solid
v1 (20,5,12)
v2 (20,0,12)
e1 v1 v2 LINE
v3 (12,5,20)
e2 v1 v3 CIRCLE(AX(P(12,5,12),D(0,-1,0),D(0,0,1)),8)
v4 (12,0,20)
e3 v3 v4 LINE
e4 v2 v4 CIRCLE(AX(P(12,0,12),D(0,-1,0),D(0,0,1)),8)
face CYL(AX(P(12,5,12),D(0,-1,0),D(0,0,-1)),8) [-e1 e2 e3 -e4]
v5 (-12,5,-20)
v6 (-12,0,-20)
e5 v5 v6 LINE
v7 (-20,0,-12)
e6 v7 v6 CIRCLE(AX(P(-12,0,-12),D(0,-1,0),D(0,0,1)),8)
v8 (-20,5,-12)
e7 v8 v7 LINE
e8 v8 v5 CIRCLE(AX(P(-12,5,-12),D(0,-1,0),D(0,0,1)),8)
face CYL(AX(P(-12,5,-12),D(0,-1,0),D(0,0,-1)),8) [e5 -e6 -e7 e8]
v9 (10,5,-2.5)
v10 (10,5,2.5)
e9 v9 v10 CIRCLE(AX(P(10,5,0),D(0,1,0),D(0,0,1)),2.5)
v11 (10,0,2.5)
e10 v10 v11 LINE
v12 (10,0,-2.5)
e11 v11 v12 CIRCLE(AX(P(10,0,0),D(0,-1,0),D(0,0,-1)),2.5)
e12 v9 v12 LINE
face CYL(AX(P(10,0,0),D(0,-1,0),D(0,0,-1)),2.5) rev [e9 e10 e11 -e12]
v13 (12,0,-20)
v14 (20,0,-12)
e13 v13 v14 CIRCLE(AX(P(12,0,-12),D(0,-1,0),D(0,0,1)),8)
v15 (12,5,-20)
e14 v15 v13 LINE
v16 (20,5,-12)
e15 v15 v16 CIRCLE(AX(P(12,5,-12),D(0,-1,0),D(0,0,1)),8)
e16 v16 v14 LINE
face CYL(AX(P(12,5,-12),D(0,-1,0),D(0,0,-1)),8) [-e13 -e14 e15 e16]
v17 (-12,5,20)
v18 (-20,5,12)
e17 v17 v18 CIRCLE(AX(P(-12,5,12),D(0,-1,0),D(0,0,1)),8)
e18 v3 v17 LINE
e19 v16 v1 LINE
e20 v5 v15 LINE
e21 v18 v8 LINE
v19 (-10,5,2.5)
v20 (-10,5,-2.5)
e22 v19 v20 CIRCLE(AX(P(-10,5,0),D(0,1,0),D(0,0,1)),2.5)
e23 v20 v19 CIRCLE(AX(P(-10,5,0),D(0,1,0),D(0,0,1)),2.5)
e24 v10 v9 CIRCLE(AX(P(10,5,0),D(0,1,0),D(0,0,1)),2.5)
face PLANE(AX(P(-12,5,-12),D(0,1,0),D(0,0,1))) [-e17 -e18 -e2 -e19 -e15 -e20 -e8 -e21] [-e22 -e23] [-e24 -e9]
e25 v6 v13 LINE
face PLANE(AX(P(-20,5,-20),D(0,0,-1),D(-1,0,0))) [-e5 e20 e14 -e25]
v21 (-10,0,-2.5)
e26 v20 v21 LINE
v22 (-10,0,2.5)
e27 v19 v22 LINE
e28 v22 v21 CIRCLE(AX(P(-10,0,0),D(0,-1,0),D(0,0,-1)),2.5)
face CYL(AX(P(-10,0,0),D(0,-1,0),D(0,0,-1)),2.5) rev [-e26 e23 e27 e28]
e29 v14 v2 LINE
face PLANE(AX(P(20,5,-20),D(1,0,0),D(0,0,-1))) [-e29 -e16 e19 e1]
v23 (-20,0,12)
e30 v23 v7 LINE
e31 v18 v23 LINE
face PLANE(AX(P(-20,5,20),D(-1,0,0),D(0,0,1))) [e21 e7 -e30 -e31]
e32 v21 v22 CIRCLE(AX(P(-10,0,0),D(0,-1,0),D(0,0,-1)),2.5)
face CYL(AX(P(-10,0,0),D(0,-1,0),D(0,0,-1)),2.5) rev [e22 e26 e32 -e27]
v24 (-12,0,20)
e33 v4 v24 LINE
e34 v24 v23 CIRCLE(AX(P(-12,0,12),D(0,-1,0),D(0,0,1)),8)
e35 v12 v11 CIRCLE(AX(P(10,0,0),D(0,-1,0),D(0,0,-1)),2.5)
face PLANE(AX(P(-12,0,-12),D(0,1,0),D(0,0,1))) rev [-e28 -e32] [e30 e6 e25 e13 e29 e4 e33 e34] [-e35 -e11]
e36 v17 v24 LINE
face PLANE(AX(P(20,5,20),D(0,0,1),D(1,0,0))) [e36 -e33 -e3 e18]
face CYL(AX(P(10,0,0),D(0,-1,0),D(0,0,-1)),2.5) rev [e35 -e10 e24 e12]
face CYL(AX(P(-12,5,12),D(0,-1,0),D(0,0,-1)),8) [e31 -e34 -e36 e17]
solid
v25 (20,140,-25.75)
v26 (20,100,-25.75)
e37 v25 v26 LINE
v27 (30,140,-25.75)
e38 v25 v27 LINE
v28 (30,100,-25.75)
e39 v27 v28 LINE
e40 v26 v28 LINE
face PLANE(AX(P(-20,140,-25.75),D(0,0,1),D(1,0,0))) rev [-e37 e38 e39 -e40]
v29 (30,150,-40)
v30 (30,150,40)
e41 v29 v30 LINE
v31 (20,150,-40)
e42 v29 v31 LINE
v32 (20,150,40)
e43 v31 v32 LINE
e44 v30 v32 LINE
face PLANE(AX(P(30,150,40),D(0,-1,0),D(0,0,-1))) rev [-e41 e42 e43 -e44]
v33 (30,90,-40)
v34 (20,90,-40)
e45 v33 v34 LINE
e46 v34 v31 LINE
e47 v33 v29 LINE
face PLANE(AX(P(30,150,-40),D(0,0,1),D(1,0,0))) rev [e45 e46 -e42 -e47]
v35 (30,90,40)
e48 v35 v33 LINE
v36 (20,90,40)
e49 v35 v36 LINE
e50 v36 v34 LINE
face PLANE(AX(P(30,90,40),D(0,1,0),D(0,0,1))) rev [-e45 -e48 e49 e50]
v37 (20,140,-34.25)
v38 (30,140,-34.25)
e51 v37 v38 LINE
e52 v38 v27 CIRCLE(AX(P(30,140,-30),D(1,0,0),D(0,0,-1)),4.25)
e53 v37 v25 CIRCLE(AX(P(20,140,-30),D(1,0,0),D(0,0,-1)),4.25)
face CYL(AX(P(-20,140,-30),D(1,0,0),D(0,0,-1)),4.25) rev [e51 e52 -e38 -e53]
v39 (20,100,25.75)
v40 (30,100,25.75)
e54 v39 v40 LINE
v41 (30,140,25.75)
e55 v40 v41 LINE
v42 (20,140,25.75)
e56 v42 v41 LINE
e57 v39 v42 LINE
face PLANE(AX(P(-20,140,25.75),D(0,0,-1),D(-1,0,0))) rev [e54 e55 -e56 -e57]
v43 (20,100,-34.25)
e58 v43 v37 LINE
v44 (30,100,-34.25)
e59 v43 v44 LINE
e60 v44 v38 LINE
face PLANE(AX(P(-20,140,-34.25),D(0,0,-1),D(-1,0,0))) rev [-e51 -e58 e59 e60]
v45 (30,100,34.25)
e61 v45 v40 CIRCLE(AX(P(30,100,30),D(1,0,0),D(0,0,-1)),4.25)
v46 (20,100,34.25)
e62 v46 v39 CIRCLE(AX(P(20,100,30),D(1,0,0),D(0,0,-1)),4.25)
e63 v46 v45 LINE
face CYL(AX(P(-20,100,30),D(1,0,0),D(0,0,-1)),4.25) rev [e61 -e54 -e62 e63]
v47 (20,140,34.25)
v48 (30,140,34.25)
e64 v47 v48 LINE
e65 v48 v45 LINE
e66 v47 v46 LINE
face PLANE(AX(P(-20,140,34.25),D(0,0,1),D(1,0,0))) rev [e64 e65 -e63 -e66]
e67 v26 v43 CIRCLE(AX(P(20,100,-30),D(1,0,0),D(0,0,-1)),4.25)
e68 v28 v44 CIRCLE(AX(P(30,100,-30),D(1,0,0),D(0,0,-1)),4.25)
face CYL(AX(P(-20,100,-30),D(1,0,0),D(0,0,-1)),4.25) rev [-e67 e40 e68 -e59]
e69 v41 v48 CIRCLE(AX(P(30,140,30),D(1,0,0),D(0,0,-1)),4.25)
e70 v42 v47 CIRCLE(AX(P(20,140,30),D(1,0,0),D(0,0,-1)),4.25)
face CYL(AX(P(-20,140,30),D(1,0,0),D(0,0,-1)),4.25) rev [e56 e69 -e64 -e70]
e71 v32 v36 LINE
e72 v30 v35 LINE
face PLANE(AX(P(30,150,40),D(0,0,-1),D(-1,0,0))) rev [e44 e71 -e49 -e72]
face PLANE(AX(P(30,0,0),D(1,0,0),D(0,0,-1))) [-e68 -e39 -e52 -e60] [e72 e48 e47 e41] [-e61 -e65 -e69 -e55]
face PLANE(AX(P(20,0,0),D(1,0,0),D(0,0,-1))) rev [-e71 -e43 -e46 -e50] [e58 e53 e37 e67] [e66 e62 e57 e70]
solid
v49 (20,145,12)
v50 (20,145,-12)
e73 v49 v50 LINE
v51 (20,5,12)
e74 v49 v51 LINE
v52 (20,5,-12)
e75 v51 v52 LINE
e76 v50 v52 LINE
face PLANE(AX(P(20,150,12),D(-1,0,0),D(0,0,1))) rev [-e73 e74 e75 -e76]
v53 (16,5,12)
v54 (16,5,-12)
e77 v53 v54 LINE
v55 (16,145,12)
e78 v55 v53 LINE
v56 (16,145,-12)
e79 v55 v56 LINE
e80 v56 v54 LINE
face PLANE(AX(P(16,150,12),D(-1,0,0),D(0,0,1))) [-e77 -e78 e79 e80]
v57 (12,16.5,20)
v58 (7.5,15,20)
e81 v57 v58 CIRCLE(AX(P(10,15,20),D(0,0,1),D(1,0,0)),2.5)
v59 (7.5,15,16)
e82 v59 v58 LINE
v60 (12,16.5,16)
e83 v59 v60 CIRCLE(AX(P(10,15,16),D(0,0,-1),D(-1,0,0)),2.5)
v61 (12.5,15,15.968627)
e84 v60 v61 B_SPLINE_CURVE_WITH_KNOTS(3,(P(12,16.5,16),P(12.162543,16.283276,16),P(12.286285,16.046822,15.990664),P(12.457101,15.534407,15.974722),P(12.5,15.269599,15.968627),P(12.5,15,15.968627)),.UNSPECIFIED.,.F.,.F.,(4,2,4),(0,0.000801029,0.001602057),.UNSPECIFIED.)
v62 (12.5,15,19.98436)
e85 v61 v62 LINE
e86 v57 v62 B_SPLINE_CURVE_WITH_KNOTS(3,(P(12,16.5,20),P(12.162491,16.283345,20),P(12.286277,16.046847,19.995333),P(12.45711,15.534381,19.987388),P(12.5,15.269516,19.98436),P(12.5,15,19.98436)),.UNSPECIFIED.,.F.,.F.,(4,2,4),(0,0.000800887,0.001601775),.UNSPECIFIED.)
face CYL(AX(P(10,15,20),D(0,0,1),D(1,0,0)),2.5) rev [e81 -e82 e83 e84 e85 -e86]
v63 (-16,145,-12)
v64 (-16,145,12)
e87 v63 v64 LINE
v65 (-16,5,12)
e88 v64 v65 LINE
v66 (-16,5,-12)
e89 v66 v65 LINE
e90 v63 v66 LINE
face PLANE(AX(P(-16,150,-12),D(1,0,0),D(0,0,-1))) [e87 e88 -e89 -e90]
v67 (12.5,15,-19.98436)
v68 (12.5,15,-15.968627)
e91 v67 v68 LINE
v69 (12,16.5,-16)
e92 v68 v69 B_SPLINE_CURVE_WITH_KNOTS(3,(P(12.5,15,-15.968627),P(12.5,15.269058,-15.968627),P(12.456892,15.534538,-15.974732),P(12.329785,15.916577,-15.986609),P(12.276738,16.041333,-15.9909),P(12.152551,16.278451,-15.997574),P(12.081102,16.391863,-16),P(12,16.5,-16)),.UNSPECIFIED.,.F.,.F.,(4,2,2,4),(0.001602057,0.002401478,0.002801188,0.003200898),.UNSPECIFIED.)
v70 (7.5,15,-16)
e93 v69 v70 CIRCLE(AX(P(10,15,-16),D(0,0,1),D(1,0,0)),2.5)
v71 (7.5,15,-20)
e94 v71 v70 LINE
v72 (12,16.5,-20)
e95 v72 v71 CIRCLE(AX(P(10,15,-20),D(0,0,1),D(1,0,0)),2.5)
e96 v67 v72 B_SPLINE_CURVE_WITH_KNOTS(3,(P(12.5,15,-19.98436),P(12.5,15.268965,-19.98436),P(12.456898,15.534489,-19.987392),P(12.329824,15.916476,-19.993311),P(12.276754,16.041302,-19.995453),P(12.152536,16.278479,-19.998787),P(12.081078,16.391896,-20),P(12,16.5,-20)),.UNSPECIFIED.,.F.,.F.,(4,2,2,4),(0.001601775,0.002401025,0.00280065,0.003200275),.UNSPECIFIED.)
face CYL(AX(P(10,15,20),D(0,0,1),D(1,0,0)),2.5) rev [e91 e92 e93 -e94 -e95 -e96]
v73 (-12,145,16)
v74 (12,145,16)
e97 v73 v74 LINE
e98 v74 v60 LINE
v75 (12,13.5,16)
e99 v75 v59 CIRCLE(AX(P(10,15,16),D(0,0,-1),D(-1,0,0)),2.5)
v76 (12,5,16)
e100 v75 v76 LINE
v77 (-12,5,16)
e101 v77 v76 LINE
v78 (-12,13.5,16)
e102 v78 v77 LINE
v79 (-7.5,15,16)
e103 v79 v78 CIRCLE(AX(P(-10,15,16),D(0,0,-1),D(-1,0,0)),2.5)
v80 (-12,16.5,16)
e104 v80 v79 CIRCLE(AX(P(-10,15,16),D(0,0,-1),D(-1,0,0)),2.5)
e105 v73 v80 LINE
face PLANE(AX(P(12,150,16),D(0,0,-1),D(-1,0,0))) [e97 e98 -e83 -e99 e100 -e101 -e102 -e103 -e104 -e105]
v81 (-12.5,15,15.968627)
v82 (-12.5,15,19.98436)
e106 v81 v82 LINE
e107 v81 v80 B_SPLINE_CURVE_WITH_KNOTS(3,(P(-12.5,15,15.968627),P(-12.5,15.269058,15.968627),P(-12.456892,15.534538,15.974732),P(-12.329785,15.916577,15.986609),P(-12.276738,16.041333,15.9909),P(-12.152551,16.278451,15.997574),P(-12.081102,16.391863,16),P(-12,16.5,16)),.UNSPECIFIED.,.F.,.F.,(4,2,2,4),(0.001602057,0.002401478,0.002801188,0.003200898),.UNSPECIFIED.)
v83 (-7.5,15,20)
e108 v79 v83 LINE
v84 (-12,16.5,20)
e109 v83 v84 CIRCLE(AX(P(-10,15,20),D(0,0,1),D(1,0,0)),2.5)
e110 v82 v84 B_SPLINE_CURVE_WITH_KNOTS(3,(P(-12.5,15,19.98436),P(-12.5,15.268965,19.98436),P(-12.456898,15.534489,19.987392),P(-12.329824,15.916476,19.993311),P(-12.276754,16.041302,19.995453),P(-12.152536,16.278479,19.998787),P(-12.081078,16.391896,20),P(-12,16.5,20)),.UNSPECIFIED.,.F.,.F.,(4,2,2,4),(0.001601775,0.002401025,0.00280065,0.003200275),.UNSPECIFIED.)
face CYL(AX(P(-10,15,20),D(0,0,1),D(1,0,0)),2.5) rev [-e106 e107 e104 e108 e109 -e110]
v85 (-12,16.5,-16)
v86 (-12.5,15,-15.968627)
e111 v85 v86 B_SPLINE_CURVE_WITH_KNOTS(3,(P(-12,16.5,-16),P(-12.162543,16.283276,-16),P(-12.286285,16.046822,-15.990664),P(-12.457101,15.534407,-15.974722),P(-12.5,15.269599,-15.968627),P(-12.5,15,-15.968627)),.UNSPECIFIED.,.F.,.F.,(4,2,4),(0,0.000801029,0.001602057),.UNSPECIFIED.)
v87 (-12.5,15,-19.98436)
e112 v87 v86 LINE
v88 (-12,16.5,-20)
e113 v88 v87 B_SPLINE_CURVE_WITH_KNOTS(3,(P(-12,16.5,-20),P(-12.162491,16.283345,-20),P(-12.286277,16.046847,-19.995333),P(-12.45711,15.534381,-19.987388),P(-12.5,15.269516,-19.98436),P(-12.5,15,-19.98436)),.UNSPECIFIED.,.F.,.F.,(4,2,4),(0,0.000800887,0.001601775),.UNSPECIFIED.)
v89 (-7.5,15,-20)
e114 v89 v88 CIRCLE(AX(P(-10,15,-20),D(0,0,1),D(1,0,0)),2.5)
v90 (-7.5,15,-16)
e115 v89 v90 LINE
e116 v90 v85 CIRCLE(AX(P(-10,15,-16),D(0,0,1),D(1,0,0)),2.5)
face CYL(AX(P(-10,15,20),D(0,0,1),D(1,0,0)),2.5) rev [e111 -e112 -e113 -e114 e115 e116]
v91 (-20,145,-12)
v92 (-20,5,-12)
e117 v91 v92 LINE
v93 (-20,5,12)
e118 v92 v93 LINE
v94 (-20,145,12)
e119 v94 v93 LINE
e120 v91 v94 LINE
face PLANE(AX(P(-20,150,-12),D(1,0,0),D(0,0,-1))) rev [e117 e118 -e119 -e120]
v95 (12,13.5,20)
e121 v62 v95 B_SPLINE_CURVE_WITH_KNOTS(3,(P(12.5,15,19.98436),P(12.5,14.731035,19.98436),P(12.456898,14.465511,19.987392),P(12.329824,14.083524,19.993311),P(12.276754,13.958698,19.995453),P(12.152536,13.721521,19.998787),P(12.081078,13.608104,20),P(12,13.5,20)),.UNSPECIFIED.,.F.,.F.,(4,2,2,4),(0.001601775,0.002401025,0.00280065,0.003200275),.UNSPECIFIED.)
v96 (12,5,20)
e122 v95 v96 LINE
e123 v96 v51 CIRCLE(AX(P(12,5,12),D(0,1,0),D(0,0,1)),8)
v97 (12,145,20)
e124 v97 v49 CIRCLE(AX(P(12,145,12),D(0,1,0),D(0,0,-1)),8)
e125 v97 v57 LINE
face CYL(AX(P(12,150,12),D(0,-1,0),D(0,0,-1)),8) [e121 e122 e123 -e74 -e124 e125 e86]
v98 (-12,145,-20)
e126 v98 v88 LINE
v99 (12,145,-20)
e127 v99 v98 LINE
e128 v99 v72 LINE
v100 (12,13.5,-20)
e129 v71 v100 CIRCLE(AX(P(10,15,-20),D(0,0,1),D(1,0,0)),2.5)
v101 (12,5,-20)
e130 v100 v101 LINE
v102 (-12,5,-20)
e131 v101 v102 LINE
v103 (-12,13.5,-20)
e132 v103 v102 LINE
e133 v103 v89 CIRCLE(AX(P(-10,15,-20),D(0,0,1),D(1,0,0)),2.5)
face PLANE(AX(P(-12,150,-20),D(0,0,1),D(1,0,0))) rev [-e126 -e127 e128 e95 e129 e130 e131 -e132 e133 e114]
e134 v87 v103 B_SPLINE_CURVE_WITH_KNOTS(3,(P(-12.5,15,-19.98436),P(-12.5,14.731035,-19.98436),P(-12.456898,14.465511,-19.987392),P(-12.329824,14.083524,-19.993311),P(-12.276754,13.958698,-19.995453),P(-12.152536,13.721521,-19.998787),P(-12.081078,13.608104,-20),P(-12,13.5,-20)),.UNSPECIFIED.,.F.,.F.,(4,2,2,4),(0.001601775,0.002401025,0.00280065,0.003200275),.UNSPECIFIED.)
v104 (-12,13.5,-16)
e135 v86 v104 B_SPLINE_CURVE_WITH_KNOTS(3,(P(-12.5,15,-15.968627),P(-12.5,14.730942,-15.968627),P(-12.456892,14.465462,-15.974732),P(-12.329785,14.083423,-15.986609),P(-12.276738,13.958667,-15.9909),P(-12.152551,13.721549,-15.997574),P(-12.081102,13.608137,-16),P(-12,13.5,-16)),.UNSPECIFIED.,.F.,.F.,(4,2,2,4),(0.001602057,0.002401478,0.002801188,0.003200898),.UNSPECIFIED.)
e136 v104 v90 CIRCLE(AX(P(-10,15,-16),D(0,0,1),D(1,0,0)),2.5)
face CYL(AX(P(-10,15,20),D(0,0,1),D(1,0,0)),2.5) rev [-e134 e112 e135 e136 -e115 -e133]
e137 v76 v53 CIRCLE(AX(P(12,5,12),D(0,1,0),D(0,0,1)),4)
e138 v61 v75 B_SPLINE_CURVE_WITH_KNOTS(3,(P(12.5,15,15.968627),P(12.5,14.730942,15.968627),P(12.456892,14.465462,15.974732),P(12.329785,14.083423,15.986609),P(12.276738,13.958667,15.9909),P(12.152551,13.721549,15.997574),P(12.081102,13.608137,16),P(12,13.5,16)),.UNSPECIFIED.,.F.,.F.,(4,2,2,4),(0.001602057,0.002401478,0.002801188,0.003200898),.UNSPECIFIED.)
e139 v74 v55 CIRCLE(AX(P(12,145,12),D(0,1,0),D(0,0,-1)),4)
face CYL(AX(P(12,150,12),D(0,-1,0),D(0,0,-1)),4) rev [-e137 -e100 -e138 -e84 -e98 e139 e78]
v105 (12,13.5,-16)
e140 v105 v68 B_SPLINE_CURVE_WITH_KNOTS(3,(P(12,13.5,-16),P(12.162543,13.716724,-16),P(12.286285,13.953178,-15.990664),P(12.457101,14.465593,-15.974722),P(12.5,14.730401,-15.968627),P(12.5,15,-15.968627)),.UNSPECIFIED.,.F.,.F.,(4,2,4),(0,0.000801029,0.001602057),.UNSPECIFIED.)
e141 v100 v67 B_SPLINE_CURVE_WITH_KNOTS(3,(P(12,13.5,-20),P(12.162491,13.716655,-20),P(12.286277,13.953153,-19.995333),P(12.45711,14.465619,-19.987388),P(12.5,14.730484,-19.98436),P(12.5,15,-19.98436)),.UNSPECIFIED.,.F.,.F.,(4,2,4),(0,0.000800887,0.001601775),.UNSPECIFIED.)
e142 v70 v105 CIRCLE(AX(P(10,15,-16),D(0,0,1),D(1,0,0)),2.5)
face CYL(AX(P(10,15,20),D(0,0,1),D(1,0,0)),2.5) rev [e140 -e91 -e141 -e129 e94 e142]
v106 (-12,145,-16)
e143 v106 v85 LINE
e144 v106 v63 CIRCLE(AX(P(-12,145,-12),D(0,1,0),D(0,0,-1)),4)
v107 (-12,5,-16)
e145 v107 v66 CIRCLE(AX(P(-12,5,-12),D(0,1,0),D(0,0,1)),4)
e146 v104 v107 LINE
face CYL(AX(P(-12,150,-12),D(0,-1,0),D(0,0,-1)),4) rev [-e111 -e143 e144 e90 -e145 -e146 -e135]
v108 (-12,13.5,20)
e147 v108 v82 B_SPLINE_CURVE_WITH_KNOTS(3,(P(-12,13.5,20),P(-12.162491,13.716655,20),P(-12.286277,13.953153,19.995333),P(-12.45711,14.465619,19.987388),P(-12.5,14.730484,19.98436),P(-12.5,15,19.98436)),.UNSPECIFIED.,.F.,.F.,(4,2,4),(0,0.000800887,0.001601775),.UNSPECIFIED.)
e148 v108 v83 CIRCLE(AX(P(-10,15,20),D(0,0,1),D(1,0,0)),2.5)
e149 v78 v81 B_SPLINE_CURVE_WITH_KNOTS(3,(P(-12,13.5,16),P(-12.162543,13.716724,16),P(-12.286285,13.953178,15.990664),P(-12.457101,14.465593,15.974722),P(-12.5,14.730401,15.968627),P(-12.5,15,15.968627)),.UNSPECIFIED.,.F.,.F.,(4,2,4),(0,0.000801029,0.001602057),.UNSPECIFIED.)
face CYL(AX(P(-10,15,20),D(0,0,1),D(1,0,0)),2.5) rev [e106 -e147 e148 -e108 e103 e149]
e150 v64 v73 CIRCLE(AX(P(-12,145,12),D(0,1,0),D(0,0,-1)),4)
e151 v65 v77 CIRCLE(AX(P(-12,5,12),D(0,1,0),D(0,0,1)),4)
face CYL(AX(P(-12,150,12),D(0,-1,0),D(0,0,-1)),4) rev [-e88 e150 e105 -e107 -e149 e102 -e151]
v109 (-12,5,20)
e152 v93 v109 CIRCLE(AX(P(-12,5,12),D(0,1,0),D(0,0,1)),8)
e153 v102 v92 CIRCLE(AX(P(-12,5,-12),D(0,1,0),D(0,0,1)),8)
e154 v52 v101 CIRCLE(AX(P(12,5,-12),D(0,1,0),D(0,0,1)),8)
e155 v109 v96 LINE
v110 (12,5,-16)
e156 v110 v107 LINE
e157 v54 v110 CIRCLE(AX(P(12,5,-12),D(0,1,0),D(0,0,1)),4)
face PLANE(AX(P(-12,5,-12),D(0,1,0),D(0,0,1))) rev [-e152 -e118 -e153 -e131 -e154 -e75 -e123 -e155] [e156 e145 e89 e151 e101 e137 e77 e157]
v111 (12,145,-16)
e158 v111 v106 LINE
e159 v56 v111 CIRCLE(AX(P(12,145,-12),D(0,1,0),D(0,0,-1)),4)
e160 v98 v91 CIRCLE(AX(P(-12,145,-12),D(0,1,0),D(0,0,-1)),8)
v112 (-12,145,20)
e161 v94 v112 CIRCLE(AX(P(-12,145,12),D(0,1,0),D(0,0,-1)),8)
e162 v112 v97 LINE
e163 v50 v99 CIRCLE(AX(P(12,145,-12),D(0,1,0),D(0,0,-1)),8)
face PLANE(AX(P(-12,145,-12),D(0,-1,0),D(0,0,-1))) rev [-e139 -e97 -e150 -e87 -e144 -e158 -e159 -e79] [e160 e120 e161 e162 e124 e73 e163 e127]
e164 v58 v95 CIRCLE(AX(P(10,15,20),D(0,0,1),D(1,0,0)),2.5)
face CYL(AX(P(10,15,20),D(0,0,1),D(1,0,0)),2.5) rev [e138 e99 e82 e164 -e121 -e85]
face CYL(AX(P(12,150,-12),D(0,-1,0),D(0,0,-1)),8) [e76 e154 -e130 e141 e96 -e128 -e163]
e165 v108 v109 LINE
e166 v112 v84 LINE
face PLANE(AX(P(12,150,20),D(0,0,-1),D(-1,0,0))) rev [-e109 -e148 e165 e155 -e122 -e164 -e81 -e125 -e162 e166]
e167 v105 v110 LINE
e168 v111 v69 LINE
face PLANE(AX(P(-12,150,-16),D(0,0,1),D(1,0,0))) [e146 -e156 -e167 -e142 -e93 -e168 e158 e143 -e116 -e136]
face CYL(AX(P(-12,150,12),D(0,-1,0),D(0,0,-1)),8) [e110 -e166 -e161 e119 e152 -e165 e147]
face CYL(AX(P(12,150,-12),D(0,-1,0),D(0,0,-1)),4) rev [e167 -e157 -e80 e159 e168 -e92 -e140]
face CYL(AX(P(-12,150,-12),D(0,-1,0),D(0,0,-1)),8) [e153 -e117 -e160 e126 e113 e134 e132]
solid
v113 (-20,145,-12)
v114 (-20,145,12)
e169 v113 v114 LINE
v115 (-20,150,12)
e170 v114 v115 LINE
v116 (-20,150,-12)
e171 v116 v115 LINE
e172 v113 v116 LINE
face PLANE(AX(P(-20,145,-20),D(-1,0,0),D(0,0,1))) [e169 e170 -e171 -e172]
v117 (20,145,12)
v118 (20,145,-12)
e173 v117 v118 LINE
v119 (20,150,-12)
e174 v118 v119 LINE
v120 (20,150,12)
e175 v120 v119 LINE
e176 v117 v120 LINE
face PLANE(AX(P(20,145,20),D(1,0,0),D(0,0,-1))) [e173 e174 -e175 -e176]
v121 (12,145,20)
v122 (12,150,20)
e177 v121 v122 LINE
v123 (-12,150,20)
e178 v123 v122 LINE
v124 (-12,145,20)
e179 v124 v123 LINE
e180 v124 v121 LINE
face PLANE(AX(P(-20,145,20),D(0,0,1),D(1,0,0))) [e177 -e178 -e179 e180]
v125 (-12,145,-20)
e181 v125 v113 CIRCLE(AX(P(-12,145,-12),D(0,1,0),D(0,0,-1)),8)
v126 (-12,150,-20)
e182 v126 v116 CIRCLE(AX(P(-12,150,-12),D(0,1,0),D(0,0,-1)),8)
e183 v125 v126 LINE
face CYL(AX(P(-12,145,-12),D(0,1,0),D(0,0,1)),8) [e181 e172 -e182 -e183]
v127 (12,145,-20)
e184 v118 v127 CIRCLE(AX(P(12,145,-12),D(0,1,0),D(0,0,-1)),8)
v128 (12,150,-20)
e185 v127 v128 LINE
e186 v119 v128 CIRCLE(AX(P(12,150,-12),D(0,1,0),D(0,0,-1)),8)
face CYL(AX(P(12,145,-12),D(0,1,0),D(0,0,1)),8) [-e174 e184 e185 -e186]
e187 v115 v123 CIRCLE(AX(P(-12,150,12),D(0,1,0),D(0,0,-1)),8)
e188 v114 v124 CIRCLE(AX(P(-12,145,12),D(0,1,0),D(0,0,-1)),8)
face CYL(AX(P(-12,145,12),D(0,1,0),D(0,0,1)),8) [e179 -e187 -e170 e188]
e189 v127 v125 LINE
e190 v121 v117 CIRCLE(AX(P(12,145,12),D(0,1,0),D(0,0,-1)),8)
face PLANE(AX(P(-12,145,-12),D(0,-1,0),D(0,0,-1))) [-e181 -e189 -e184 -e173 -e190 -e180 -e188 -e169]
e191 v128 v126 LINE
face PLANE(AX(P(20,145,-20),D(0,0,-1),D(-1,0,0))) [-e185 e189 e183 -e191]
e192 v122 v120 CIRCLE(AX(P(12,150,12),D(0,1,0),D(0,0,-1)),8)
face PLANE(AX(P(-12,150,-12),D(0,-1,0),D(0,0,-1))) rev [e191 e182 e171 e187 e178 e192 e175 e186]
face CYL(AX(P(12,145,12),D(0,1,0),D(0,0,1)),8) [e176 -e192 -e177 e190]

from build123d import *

# Parameters (mm, degrees)
F_40_X_40_X_4_0_1_DEPTH     = 150
SKETCH_3_W                  = 80
SKETCH_3_H                  = 60
EXTRUDE_1_DEPTH             = 10
CUT_EXTRUDE_2_DEPTH         = 164.095064303
SKETCH_14_W                 = 2.5
SKETCH_14_H                 = 60
HOLE_WIZARD_M6_1_AT_2_COUNT = 2
HOLE_WIZARD_M6_1_AT_2_PITCH = 20
END_CAP_1_THICKNESS         = 5
HOLE_WIZARD_M6_2_AT_2_COUNT = 2
HOLE_WIZARD_M6_2_AT_2_PITCH = 20
END_CAP_2_THICKNESS         = 5


with BuildPart() as part:
    # Sketch1 → 方管 40 X 40 X 4.0(1) (new body)
    with BuildSketch(Plane.ZX):
        with BuildLine():
            Line((-12, -20), (12, -20))
            ThreePointArc((12, -20), (17.656854249, -17.656854249), (20, -12))
            Line((20, -12), (20, 12))
            ThreePointArc((20, 12), (17.656854249, 17.656854249), (12, 20))
            Line((12, 20), (-12, 20))
            ThreePointArc((-12, 20), (-17.656854249, 17.656854249), (-20, 12))
            Line((-20, 12), (-20, -12))
            ThreePointArc((-20, -12), (-17.656854249, -17.656854249), (-12, -20))
        make_face()
        with BuildLine():
            Line((-12, -16), (12, -16))
            ThreePointArc((12, -16), (14.828427125, -14.828427125), (16, -12))
            Line((16, -12), (16, 12))
            ThreePointArc((16, 12), (14.828427125, 14.828427125), (12, 16))
            Line((12, 16), (-12, 16))
            ThreePointArc((-12, 16), (-14.828427125, 14.828427125), (-16, 12))
            Line((-16, 12), (-16, -12))
            ThreePointArc((-16, -12), (-14.828427125, -14.828427125), (-12, -16))
        make_face(mode=Mode.SUBTRACT)
    extrude(amount=F_40_X_40_X_4_0_1_DEPTH)

    # 草图14 → M6 螺纹孔1 (revolve, cut)
    with BuildSketch(Plane(origin=(-10, 15, 20), x_dir=(0, -1, 0), z_dir=(1, 0, 0))):
        with Locations((1.25, 30)):
            Rectangle(SKETCH_14_W, SKETCH_14_H)
    hole_wizard_m6_1 = revolve(axis=Axis((-10, 15, 26.35), (0, 0, -1)), mode=Mode.SUBTRACT)

    # M6 螺纹孔1 at 2: M6 螺纹孔1 ×2
    with Locations(*[(i * HOLE_WIZARD_M6_1_AT_2_PITCH, 0, 0) for i in range(1, HOLE_WIZARD_M6_1_AT_2_COUNT)]):
        add(hole_wizard_m6_1, mode=Mode.SUBTRACT)


with BuildPart() as body_2:
    # 草图3 → 凸台-拉伸1 (new body)
    with BuildSketch(Plane(origin=(20, 0, 0), x_dir=(0, 0, -1), z_dir=(1, 0, 0))):
        with Locations((0, 120)):
            Rectangle(SKETCH_3_W, SKETCH_3_H)
    extrude(amount=EXTRUDE_1_DEPTH)

    # 草图12 → 切除-拉伸2 (cut, through all)
    with BuildSketch(Plane(origin=(30, 0, 0), x_dir=(0, 0, -1), z_dir=(1, 0, 0))):
        with BuildLine():
            Line((-25.75, 140), (-25.75, 100))
            ThreePointArc((-25.75, 100), (-30, 95.75), (-34.25, 100))
            Line((-34.25, 100), (-34.25, 140))
            ThreePointArc((-34.25, 140), (-30, 144.25), (-25.75, 140))
        make_face()
        with BuildLine():
            Line((34.25, 140), (34.25, 100))
            ThreePointArc((34.25, 100), (30, 95.75), (25.75, 100))
            Line((25.75, 100), (25.75, 140))
            ThreePointArc((25.75, 140), (30, 144.25), (34.25, 140))
        make_face()
    extrude(amount=-CUT_EXTRUDE_2_DEPTH, mode=Mode.SUBTRACT)


with BuildPart() as body_3:
    # End Cap 1: an end cap: a plate 5.0 thick on the member's open end, its outline the end's outer outline
    end_cap_1_end = part.part.faces().sort_by_distance((-16, 0, -16))[0]
    add(extrude(Face(end_cap_1_end.outer_wire()), amount=END_CAP_1_THICKNESS, dir=(0, 1, 0)))

    # 草图17 → M6 螺纹孔2 (revolve, cut)
    with BuildSketch(Plane(origin=(-10, 0, 0), x_dir=(0, 0, -1), z_dir=(1, 0, 0))):
        Polygon((0, 0), (0, 16.502151548), (2.5, 15), (2.5, 0), align=None)
    hole_wizard_m6_2 = revolve(axis=Axis((-10, -6.35, 0), (0, 1, 0)), mode=Mode.SUBTRACT)

    # M6 螺纹孔2 at 2: M6 螺纹孔2 ×2
    with Locations(*[(i * HOLE_WIZARD_M6_2_AT_2_PITCH, 0, 0) for i in range(1, HOLE_WIZARD_M6_2_AT_2_COUNT)]):
        add(hole_wizard_m6_2, mode=Mode.SUBTRACT)


with BuildPart() as part_1:
    add(part.part)

    # End Cap 1 3
    split(bisect_by=Plane(origin=(0, 5, 0), x_dir=(-1, 0, 0), z_dir=(0, 1, 0)), keep=Keep.TOP)


with BuildPart() as body_4:
    # End Cap 2: an end cap: a plate 5.0 thick on the member's open end, its outline the end's outer outline
    end_cap_2_end = part_1.part.faces().sort_by_distance((-16, 150, -16))[0]
    add(extrude(Face(end_cap_2_end.outer_wire()), amount=END_CAP_2_THICKNESS, dir=(0, -1, 0)))


with BuildPart() as part_2:
    add(part_1.part)

    # End Cap 2 3
    split(bisect_by=Plane.XZ.offset(-145), keep=Keep.TOP)


solid = Compound([body_2.part, body_3.part, body_4.part, part_2.part])
